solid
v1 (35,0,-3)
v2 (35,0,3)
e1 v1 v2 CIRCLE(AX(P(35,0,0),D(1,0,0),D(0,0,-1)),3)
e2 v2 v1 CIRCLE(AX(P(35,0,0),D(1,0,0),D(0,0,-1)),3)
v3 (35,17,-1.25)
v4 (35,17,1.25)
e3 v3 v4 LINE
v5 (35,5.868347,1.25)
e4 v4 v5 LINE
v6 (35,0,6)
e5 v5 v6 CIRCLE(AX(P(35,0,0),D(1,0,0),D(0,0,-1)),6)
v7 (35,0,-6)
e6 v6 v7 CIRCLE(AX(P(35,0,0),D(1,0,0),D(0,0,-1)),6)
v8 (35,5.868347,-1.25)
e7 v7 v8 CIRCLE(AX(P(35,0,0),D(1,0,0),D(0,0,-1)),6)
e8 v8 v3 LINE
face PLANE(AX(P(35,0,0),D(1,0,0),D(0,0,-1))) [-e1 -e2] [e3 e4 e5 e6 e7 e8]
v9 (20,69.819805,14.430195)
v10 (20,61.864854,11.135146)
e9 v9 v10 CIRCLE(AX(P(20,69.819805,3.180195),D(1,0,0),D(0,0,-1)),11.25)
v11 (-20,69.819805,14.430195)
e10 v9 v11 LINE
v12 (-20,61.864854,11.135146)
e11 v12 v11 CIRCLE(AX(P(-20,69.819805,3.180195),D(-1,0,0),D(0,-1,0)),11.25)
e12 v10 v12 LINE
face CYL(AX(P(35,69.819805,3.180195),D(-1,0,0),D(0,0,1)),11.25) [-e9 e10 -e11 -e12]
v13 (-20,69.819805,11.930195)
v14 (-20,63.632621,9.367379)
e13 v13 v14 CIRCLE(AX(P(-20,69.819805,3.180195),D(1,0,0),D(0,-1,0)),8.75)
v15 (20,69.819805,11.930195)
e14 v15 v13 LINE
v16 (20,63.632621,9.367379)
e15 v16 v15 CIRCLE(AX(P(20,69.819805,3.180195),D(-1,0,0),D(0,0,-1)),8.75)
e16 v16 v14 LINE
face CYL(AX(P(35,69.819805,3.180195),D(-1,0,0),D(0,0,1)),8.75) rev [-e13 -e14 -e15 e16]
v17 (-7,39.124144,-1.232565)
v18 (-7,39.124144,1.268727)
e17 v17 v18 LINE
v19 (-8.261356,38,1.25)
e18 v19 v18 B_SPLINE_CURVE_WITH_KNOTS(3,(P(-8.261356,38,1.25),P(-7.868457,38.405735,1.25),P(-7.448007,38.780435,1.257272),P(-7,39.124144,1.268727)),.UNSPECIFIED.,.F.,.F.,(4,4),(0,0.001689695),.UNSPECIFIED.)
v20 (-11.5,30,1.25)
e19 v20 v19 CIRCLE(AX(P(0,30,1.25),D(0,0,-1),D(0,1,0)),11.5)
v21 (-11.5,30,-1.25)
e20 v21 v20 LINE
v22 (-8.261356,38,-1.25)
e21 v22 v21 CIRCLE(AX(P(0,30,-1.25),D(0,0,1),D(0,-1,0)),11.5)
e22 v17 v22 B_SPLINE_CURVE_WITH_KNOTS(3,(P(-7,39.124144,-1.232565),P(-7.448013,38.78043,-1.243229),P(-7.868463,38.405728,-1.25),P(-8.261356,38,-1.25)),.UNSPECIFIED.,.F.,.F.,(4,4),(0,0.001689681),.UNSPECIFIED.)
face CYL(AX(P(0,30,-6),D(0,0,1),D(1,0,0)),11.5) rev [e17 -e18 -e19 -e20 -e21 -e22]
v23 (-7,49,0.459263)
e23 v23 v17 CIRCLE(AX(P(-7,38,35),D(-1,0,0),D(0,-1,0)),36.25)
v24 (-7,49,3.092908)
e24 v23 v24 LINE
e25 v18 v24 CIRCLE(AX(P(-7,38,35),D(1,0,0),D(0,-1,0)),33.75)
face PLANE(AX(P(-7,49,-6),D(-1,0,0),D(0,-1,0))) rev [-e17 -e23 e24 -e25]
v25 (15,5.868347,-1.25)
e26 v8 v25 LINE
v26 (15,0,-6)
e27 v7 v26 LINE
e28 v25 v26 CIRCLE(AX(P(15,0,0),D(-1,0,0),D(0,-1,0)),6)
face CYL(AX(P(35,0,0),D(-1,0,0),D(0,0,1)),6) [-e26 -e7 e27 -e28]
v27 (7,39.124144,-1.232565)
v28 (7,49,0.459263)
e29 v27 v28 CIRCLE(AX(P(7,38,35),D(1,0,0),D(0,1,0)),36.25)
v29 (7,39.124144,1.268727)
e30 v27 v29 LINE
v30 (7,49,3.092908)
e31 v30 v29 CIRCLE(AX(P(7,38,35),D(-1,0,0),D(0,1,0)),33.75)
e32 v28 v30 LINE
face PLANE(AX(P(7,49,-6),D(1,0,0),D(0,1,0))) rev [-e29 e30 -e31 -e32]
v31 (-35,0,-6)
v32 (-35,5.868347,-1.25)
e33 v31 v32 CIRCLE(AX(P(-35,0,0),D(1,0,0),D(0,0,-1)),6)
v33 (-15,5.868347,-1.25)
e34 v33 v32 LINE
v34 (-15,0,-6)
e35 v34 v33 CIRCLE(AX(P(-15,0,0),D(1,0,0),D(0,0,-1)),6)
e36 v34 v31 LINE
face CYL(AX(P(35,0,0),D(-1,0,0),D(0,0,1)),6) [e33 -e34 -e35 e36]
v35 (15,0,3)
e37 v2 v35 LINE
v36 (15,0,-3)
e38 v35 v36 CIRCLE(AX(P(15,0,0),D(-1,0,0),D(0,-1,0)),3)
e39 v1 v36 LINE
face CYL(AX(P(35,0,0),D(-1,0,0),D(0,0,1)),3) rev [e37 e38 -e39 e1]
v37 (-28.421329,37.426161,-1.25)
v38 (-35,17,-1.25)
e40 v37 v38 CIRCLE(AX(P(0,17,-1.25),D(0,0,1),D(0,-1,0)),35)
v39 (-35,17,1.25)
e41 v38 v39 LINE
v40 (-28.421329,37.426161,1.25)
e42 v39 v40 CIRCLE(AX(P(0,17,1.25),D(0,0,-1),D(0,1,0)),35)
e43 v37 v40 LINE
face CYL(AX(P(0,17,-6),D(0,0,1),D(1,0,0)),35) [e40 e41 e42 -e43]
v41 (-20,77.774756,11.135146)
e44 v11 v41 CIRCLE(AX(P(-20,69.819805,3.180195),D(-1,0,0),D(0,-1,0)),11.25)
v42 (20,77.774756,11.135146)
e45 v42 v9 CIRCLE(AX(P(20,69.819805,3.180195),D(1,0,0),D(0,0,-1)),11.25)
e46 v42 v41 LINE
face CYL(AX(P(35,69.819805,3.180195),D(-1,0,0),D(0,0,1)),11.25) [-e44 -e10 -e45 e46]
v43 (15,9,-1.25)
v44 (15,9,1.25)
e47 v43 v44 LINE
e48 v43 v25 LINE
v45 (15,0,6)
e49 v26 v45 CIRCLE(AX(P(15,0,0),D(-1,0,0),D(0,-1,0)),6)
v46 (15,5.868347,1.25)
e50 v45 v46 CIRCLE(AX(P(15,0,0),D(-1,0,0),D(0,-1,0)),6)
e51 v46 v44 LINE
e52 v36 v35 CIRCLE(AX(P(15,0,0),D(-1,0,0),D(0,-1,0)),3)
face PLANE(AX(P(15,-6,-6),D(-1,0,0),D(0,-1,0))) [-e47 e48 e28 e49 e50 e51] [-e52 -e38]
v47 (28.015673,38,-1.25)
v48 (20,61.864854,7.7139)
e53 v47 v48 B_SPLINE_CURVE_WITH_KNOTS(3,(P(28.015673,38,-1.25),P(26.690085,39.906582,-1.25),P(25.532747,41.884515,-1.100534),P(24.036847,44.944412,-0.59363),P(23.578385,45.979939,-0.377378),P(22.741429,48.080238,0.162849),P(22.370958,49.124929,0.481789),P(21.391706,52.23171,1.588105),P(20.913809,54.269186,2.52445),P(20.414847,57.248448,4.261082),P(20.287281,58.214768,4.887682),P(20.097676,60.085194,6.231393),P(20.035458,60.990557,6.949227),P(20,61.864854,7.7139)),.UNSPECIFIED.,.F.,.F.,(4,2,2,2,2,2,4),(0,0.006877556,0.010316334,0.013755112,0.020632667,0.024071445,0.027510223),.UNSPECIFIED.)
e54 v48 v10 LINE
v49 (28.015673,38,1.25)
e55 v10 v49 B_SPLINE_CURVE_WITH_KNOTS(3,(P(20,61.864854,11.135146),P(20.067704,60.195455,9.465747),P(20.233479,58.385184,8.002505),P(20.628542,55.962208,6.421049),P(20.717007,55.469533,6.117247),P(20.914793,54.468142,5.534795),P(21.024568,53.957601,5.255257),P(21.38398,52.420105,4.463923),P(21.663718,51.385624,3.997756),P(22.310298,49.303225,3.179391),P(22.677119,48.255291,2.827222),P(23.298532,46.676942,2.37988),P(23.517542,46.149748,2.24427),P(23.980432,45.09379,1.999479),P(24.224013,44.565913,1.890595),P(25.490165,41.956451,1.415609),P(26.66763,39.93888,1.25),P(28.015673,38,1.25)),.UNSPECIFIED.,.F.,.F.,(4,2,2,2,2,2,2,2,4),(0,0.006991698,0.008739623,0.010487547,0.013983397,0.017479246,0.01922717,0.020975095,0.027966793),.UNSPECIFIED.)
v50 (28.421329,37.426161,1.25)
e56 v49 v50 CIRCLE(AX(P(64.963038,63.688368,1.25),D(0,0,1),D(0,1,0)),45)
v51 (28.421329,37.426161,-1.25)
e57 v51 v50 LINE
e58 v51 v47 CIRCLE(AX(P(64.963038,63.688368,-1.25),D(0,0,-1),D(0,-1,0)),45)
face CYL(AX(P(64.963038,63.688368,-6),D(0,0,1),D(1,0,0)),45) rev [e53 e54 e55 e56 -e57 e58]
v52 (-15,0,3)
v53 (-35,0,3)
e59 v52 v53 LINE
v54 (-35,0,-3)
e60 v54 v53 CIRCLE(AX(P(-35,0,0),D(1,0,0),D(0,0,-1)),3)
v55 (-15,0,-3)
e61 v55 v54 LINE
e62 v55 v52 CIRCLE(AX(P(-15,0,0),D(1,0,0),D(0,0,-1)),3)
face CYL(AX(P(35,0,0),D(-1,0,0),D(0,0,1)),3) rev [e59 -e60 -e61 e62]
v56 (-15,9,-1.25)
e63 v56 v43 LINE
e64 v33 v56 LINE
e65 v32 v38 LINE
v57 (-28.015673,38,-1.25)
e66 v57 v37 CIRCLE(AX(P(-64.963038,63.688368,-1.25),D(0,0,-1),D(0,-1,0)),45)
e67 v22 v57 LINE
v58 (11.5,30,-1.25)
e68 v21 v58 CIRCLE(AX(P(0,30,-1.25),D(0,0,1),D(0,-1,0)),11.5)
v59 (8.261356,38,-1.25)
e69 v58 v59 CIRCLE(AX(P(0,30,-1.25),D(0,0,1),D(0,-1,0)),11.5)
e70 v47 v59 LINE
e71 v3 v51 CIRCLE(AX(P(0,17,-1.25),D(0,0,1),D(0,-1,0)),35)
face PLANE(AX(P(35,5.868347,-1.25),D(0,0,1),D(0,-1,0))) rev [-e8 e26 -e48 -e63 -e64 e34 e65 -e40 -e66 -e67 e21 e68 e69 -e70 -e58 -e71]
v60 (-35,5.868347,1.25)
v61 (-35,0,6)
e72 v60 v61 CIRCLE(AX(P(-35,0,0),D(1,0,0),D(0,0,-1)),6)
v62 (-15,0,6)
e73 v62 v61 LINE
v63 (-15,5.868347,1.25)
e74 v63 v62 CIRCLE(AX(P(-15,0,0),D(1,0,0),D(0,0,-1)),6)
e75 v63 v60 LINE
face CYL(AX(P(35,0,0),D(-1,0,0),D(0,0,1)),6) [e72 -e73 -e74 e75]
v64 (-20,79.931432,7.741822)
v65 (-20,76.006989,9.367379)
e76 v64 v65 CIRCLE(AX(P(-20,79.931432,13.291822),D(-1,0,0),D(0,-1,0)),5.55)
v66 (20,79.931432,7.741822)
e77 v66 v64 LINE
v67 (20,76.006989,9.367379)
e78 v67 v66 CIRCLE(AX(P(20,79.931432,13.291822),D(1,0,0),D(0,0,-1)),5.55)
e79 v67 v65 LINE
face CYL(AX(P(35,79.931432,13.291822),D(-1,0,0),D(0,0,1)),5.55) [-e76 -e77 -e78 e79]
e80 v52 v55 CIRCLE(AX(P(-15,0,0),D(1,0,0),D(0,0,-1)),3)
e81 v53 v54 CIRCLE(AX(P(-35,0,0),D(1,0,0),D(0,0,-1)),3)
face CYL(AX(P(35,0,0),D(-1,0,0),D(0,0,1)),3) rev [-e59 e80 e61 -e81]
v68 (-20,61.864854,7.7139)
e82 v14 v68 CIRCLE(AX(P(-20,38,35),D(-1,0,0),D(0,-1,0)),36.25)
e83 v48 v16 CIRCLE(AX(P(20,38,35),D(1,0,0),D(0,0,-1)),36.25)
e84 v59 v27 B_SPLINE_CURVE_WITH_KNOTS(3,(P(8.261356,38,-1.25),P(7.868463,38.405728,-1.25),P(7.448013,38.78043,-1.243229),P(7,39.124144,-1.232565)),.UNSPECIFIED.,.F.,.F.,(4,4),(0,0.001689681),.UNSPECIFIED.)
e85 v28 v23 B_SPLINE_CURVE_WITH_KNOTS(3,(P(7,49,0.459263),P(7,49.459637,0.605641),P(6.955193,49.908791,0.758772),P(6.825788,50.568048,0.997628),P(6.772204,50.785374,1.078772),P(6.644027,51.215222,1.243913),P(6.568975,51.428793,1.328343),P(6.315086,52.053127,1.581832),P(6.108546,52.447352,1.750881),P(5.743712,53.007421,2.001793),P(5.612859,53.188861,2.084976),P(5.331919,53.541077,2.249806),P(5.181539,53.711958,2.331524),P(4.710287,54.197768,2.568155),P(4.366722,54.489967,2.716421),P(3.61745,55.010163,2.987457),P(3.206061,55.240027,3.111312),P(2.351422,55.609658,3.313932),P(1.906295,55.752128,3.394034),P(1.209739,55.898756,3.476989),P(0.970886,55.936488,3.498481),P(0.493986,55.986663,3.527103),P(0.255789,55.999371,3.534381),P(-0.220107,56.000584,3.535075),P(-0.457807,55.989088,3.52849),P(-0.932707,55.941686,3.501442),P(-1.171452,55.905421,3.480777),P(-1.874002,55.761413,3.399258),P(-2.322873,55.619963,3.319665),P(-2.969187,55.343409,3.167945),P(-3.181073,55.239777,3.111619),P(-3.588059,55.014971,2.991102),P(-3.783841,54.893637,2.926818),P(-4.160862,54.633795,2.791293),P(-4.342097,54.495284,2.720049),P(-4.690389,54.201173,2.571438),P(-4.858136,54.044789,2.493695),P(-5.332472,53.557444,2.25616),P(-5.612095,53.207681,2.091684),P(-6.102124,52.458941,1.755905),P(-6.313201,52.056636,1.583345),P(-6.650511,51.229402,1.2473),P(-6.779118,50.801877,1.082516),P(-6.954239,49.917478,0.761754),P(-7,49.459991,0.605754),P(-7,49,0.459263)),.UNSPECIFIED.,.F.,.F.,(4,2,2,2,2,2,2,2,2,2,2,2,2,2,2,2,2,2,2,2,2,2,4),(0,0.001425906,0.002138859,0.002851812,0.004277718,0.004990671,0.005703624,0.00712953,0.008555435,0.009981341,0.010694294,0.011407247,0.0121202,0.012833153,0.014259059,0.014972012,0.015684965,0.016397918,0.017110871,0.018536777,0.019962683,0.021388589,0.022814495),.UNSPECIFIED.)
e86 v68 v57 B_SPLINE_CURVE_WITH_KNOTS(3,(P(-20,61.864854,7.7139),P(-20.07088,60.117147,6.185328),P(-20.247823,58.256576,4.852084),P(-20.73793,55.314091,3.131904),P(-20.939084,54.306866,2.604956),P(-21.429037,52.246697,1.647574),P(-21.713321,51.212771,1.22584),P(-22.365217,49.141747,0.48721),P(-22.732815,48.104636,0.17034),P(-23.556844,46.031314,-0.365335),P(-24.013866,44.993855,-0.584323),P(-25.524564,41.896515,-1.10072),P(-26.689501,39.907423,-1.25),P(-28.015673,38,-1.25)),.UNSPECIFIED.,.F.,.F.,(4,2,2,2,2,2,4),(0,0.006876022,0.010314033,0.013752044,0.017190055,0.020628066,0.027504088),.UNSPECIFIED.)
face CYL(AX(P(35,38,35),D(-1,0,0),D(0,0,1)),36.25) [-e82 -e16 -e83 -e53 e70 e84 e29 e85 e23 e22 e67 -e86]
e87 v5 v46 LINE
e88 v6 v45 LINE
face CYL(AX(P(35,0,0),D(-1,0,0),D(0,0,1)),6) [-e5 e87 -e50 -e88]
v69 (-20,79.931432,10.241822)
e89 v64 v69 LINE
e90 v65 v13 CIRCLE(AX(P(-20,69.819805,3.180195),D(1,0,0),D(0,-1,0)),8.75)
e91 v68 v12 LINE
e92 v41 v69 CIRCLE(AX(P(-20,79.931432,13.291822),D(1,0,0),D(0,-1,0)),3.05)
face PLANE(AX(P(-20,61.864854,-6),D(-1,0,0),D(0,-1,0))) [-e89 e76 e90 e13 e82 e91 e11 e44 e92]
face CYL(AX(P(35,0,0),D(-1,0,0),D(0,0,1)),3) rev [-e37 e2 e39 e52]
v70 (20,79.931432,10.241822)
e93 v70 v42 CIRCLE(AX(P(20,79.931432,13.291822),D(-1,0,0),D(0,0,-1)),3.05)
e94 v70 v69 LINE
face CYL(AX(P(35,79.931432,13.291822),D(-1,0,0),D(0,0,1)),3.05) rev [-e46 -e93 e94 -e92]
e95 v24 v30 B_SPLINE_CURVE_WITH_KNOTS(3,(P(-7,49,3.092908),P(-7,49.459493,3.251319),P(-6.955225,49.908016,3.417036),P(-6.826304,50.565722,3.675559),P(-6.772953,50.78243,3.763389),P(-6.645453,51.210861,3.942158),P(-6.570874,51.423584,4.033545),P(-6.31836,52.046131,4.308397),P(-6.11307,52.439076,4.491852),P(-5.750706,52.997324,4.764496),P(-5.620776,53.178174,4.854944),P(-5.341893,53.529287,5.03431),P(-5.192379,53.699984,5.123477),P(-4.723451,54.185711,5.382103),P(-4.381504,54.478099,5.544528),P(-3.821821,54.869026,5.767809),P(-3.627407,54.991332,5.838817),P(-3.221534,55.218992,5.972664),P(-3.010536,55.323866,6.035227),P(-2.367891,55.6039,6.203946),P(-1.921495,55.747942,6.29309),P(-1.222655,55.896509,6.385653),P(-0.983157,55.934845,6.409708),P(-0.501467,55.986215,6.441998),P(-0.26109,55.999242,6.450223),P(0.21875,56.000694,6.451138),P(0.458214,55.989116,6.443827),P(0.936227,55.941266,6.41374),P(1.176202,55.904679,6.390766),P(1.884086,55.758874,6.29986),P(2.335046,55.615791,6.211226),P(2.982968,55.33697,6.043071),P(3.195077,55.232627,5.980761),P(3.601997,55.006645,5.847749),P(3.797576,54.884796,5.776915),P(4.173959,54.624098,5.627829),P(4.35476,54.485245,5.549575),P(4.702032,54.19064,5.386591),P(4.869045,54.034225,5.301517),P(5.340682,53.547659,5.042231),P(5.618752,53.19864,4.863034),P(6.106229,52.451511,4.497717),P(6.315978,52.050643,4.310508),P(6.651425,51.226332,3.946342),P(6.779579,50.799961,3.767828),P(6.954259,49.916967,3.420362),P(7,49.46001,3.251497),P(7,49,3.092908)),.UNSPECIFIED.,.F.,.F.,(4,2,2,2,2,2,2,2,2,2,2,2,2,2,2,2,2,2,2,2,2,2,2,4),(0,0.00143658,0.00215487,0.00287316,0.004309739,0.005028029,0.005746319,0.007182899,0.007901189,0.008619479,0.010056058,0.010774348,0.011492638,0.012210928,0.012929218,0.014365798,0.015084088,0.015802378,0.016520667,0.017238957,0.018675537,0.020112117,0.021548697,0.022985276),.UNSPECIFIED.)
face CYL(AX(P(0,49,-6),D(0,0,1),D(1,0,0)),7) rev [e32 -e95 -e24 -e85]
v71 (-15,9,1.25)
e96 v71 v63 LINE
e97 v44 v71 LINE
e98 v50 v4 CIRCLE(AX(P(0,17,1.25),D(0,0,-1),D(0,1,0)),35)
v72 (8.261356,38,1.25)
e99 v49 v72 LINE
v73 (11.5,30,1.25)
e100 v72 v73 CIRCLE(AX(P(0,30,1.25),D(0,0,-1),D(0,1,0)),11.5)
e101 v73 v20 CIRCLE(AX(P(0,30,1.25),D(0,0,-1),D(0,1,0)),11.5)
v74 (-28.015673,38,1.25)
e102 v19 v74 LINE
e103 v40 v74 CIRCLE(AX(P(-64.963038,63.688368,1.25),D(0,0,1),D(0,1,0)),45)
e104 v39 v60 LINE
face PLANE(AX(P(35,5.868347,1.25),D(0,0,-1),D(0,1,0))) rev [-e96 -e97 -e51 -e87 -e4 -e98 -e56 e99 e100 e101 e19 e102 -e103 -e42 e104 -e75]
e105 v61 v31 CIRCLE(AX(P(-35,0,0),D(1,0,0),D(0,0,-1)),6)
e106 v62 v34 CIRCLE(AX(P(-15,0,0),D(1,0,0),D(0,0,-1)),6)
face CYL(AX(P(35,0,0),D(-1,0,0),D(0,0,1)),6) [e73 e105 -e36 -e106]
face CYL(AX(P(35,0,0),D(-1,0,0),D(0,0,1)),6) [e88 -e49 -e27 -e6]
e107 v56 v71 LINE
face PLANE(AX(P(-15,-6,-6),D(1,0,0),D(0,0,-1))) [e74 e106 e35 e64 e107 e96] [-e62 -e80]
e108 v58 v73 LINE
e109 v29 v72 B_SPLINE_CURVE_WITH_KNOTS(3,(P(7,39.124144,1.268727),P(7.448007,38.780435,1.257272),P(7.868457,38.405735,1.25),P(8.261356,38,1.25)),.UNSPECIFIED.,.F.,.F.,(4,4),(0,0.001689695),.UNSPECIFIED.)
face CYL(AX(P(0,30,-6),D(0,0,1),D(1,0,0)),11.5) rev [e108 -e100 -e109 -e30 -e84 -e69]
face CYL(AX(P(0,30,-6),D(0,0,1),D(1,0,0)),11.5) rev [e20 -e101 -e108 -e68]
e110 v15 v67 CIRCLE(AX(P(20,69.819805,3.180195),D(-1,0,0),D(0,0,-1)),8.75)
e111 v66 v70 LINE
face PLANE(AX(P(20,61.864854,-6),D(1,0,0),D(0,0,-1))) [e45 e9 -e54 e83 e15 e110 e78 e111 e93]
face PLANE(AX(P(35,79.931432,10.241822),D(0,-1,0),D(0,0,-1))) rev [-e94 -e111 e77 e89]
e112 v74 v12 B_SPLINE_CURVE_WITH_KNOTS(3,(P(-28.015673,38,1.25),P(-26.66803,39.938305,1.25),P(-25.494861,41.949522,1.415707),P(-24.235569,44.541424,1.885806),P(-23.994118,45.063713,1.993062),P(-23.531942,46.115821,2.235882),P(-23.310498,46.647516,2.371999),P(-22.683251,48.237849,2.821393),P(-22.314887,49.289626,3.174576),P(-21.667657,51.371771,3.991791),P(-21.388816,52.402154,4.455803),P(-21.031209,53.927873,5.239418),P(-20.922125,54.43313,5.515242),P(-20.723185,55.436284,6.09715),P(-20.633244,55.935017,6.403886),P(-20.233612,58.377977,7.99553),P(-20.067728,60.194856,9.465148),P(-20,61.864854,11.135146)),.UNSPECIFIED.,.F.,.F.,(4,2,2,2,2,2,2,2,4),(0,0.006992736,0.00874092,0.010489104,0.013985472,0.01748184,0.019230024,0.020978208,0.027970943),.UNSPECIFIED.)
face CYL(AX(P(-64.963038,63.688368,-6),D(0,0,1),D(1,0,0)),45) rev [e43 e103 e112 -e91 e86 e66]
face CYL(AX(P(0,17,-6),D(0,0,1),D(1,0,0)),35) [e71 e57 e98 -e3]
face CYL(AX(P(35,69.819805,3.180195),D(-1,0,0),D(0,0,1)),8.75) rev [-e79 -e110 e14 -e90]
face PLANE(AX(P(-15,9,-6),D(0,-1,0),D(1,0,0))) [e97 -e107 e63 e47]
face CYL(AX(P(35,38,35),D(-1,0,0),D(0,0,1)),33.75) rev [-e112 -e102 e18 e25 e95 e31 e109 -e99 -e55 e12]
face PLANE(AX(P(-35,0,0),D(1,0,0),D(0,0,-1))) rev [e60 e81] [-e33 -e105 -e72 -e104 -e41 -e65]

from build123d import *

# Parameters (mm, degrees)
BRACKET_SIDE_PROFILE_SKETCH_R        = 3
BRACKET_BODY_EXTRUDE_70MM_DEPTH      = 35
OUTLINE_AND_KEYHOLE_CUT_DEPTH        = 89.24823725
OUTLINE_AND_KEYHOLE_CUT_DEPTH_BACK   = 89.24823725
OUTLINE_AND_KEYHOLE_SKETCH_OUTSIDE_W = 94.54
OUTLINE_AND_KEYHOLE_SKETCH_OUTSIDE_H = 110.471


with BuildPart() as part:
    # Bracket Side Profile Sketch → Bracket Body Extrude 70mm (new, symmetric)
    with BuildSketch(Plane(origin=(0, 0, 0), x_dir=(0, 0, -1), z_dir=(1, 0, 0))):
        with BuildLine():
            Line((1.25, 5.868347297), (1.25, 38))
            ThreePointArc((1.25, 38), (-1.509366946, 51.872274423), (-9.367379182, 63.632620818))
            ThreePointArc((-9.367379182, 63.632620818), (-11.930194847, 69.819805153), (-9.367379182, 76.006989489))
            ThreePointArc((-9.367379182, 76.006989489), (-8.164290412, 77.807539075), (-7.741821818, 79.931432124))
            Line((-7.741821818, 79.931432124), (-10.241821818, 79.931432124))
            ThreePointArc((-10.241821818, 79.931432124), (-10.473989243, 78.764247656), (-11.135146135, 77.774756442))
            ThreePointArc((-11.135146135, 77.774756442), (-14.430194847, 69.819805153), (-11.135146135, 61.864853865))
            ThreePointArc((-11.135146135, 61.864853865), (-3.819065778, 50.915565842), (-1.25, 38))
            Line((-1.25, 38), (-1.25, 5.868347297))
            ThreePointArc((-1.25, 5.868347297), (0, -6), (1.25, 5.868347297))
        make_face()
        Circle(BRACKET_SIDE_PROFILE_SKETCH_R, mode=Mode.SUBTRACT)
    extrude(amount=BRACKET_BODY_EXTRUDE_70MM_DEPTH, both=True)

    # Outline and Keyhole Sketch outside → Outline and Keyhole Cut (cut, two sides: drawn at the far end of the back side and taken through both)
    # profile 1 of 2: a face of its own
    with BuildSketch(Plane.XY.offset(1.25).offset(-OUTLINE_AND_KEYHOLE_CUT_DEPTH_BACK)):
        with Locations((0, 36.9655)):
            Rectangle(OUTLINE_AND_KEYHOLE_SKETCH_OUTSIDE_W, OUTLINE_AND_KEYHOLE_SKETCH_OUTSIDE_H)
        with BuildLine():
            Line((35, -6), (35, 17))
            ThreePointArc((35, 17), (33.314760402, 27.729712921), (28.421329179, 37.426160865))
            ThreePointArc((28.421329179, 37.426160865), (22.418139751, 49.027821234), (20, 61.864853865))
            Line((20, 61.864853865), (20, 79.931432124))
            Line((20, 79.931432124), (-20, 79.931432124))
            Line((-20, 79.931432124), (-20, 61.864853865))
            ThreePointArc((-20, 61.864853865), (-22.418139751, 49.027821234), (-28.421329179, 37.426160865))
            ThreePointArc((-28.421329179, 37.426160865), (-33.314760402, 27.729712921), (-35, 17))
            Line((-35, 17), (-35, -6))
            Line((-35, -6), (-15, -6))
            Line((-15, -6), (-15, 9))
            Line((-15, 9), (15, 9))
            Line((15, 9), (15, -6))
            Line((15, -6), (35, -6))
        make_face(mode=Mode.SUBTRACT)
    # profile 2 of 2: a face of its own
    with BuildSketch(Plane.XY.offset(1.25).offset(-OUTLINE_AND_KEYHOLE_CUT_DEPTH_BACK)):
        with BuildLine():
            Line((7, 49), (7, 39.124143795))
            ThreePointArc((7, 39.124143795), (0, 18.5), (-7, 39.124143795))
            Line((-7, 39.124143795), (-7, 49))
            ThreePointArc((-7, 49), (0, 56), (7, 49))
        make_face()
    extrude(amount=OUTLINE_AND_KEYHOLE_CUT_DEPTH + OUTLINE_AND_KEYHOLE_CUT_DEPTH_BACK, mode=Mode.SUBTRACT)


solid = part.part
